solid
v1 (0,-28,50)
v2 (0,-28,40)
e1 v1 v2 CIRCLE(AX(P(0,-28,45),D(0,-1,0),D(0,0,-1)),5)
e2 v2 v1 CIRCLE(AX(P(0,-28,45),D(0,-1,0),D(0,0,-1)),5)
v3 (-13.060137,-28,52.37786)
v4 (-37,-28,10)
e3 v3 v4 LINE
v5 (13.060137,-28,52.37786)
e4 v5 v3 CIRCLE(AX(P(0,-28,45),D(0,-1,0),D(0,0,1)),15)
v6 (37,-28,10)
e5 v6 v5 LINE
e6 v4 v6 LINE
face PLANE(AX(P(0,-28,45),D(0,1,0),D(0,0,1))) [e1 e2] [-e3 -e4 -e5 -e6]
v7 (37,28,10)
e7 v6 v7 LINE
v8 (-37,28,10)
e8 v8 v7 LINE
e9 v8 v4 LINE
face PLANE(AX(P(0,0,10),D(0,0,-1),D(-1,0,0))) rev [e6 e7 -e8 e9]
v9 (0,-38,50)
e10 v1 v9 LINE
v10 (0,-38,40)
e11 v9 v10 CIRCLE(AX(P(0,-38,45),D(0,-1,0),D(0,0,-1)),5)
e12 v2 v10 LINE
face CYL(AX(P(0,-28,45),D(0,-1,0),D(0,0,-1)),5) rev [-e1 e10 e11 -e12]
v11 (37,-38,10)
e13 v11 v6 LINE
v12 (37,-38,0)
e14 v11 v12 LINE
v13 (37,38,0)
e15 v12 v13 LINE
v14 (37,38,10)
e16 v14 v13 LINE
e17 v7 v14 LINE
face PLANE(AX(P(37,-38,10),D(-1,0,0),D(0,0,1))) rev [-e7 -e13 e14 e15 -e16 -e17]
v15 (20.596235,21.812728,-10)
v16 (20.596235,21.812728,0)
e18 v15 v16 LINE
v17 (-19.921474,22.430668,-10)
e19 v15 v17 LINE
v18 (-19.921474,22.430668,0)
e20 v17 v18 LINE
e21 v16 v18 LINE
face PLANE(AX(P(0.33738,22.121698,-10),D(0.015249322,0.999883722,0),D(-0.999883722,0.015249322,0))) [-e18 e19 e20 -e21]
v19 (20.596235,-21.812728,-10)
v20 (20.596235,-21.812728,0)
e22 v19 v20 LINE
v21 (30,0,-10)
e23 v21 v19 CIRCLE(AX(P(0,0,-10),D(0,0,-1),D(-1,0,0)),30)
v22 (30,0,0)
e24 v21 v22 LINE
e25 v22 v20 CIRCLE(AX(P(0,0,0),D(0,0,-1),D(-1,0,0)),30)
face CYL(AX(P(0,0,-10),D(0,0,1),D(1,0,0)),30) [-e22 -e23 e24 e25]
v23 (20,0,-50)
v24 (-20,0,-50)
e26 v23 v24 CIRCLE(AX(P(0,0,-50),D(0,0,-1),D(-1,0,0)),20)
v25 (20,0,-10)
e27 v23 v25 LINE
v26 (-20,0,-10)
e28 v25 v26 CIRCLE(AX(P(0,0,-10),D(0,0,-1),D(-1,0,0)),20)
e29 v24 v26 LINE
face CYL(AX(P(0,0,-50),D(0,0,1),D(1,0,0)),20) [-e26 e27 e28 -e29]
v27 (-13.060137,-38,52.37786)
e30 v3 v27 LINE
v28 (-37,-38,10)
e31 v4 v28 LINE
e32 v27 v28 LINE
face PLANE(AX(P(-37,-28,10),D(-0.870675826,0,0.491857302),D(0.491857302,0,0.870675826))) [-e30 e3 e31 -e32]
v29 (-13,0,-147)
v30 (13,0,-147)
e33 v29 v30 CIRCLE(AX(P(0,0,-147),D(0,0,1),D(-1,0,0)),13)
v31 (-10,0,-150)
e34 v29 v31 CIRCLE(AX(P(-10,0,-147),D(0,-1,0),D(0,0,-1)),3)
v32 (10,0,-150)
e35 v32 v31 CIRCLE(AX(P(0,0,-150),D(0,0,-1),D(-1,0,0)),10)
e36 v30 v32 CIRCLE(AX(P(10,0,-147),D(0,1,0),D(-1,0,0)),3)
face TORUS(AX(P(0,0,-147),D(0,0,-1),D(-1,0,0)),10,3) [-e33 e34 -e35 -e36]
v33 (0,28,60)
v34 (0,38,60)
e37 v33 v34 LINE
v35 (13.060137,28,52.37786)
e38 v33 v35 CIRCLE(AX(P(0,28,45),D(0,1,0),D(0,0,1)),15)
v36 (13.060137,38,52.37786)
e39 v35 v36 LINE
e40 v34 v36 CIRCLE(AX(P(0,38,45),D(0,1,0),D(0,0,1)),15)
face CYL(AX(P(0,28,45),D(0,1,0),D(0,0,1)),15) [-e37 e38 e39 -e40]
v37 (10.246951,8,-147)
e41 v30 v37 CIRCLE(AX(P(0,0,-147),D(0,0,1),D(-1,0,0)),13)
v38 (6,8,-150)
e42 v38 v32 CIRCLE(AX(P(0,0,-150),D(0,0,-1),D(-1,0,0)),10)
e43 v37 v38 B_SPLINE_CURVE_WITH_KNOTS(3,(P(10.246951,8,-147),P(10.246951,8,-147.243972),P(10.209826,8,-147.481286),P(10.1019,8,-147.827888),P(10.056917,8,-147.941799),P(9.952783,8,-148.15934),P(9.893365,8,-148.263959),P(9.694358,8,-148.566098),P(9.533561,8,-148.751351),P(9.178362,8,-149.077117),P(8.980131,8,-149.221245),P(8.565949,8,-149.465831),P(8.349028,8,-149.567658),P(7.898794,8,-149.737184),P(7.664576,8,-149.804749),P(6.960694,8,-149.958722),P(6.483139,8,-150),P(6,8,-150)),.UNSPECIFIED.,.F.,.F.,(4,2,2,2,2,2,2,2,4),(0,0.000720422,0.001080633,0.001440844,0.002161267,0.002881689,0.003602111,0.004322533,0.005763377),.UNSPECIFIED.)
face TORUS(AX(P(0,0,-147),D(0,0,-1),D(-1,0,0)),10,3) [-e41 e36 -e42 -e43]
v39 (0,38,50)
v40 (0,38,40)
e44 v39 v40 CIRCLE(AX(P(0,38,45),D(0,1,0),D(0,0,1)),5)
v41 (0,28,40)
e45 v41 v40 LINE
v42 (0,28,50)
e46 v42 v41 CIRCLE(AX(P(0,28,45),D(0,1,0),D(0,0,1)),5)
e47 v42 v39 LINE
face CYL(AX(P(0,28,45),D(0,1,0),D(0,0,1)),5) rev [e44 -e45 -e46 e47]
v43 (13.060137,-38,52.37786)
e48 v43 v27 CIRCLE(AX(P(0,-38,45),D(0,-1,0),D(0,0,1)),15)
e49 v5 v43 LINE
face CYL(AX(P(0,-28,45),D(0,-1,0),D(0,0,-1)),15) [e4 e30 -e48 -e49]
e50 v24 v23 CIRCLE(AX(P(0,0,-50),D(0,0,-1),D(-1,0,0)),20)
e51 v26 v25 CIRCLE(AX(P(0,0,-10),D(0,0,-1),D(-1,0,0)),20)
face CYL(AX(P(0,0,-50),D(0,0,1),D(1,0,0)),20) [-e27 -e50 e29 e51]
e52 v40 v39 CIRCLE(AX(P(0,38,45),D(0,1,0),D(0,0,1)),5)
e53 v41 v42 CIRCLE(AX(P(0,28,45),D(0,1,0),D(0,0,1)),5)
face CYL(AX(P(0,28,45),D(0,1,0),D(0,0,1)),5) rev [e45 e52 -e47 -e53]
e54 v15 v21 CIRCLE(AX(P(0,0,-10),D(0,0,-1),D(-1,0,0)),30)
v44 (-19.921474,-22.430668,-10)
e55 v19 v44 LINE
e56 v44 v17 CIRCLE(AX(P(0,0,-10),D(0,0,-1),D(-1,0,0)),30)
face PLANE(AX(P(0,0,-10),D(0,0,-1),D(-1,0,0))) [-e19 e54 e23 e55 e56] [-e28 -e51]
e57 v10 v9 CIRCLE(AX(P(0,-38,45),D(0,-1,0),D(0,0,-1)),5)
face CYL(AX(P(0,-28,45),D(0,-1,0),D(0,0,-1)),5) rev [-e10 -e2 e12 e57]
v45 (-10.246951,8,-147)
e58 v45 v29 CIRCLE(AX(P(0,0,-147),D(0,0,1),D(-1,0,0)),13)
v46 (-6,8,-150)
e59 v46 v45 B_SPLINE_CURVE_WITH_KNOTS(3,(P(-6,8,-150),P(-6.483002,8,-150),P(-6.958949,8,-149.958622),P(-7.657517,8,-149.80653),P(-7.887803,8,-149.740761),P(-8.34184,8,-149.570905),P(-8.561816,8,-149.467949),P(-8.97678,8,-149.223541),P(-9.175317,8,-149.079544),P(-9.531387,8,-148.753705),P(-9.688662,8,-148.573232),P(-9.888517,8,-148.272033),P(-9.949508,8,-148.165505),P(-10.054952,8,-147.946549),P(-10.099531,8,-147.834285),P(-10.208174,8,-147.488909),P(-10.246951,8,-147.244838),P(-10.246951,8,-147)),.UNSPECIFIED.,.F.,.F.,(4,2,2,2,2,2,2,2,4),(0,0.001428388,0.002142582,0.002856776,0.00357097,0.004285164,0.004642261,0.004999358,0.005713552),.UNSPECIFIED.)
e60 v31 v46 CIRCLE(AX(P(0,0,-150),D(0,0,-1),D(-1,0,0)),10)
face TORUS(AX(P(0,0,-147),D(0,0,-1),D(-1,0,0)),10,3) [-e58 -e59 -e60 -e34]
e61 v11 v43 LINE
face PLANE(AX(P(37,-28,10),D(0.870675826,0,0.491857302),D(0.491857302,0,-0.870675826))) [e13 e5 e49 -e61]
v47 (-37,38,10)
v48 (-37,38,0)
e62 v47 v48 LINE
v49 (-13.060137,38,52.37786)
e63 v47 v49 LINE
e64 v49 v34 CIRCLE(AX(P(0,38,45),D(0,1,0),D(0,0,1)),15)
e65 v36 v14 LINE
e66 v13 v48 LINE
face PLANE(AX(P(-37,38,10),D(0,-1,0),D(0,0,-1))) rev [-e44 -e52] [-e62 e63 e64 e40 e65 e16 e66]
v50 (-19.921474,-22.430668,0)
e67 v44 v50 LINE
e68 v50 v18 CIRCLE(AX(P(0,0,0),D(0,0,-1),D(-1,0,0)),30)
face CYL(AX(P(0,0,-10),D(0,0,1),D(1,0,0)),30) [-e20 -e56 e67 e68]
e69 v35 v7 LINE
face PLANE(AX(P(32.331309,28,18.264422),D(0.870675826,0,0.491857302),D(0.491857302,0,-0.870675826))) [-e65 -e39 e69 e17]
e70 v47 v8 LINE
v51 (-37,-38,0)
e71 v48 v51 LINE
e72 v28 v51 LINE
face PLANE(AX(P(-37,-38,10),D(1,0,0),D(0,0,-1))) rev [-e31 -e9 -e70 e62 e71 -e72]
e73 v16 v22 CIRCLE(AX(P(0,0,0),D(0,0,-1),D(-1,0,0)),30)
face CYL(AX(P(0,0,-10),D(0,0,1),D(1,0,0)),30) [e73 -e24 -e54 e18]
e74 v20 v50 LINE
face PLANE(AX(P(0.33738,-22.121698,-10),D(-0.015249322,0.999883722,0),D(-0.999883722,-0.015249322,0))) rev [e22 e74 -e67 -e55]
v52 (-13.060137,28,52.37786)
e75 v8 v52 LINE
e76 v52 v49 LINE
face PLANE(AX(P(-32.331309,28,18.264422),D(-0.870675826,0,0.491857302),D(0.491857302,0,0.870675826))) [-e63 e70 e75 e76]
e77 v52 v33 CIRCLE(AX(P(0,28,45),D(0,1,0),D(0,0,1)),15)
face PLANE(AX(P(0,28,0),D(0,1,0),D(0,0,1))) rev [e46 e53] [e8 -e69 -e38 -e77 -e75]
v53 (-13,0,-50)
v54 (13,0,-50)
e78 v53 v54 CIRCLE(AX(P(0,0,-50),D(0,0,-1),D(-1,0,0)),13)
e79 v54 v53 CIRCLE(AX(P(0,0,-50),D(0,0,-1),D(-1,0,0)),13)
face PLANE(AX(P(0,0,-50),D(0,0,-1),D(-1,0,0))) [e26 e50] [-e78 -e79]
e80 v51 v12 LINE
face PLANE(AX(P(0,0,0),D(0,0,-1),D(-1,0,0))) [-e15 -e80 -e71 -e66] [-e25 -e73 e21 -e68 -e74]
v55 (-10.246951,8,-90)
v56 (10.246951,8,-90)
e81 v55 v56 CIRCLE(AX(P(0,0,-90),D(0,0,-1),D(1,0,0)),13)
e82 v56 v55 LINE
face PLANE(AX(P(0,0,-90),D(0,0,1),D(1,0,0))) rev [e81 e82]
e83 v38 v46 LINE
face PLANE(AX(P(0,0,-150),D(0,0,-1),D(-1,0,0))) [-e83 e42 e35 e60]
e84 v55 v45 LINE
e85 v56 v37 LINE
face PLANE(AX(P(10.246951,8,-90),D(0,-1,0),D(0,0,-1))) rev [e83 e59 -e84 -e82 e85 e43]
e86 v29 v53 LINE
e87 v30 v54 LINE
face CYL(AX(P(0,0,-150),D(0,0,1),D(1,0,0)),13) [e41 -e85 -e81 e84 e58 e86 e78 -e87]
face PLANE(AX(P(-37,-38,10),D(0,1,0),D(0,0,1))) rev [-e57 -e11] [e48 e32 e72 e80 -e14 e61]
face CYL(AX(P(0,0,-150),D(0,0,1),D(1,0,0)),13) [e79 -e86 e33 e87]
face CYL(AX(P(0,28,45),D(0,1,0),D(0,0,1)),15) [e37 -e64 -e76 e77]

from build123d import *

# Parameters (mm, degrees)
BASE_PLATE_SKETCH_W    = 74
BASE_PLATE_SKETCH_H    = 76
BASE_PLATE_DEPTH       = 10
FLANGE_EAR_A_SKETCH_R  = 5
FLANGE_EAR_A_DEPTH     = 10
FLANGE_START           = -10
FLANGE_EAR_B_SKETCH_R  = 5
FLANGE_EAR_B_DEPTH     = 10
TRANSITION_BOSS_DEPTH  = 10
HUB_40_SKETCH_R        = 20
HUB_40_DEPTH           = 40
SHAFT_26_SKETCH_R      = 13
SHAFT_26_DEPTH         = 100
SHAFT_START            = -60
SHAFT_FLAT_CUT_DEPTH   = 60
SHAFT_EDGE_FILLET_R3_R = 3


with BuildPart() as part:
    # Base Plate Sketch → Base Plate (new body)
    with BuildSketch(Plane.XY):
        Rectangle(BASE_PLATE_SKETCH_W, BASE_PLATE_SKETCH_H)
    extrude(amount=BASE_PLATE_DEPTH)

    # Flange Ear A Sketch → Flange Ear A (add)
    with BuildSketch(Plane(origin=(0, 38, 0), x_dir=(1, 0, 0), z_dir=(0, 1, 0))):
        with BuildLine():
            Line((-37, -10), (-13.060137394, -52.377859531))
            ThreePointArc((-13.060137394, -52.377859531), (0, -60), (13.060137394, -52.377859531))
            Line((13.060137394, -52.377859531), (37, -10))
            Line((37, -10), (-37, -10))
        make_face()
        with Locations(Location((0, -45, 0), (0, 0, 270))):
            Circle(FLANGE_EAR_A_SKETCH_R, mode=Mode.SUBTRACT)
    extrude(amount=-FLANGE_EAR_A_DEPTH)

    # Flange Ear B Sketch → Flange Ear B (add)
    with BuildSketch(Plane.XZ.offset(38).offset(FLANGE_START)):
        with BuildLine():
            Line((-37, 10), (-13.060137394, 52.377859531))
            ThreePointArc((-13.060137394, 52.377859531), (0, 60), (13.060137394, 52.377859531))
            Line((13.060137394, 52.377859531), (37, 10))
            Line((37, 10), (-37, 10))
        make_face()
        with Locations(Location((0, 45, 0), (0, 0, 90))):
            Circle(FLANGE_EAR_B_SKETCH_R, mode=Mode.SUBTRACT)
    extrude(amount=FLANGE_EAR_B_DEPTH)

    # Transition Boss Sketch → Transition Boss (add)
    with BuildSketch(Plane(origin=(0, 0, 0), x_dir=(-1, 0, 0), z_dir=(0, 0, -1))):
        with BuildLine():
            Line((19.921474427, 22.430667771), (-20.596234674, 21.812728331))
            ThreePointArc((-20.596234674, 21.812728331), (-22.10962434, 20.277191904), (-23.508824666, 18.636930081))
            ThreePointArc((-23.508824666, 18.636930081), (-30, 0), (-23.508824666, -18.636930081))
            ThreePointArc((-23.508824666, -18.636930081), (-22.10962434, -20.277191904), (-20.596234674, -21.812728331))
            Line((-20.596234674, -21.812728331), (19.921474427, -22.430667771))
            ThreePointArc((19.921474427, -22.430667771), (21.797840059, -20.611990897), (23.508824666, -18.636930081))
            ThreePointArc((23.508824666, -18.636930081), (30, 0), (23.508824666, 18.636930081))
            ThreePointArc((23.508824666, 18.636930081), (21.797840059, 20.611990897), (19.921474427, 22.430667771))
        make_face()
    extrude(amount=TRANSITION_BOSS_DEPTH)

    # Hub _40 Sketch → Hub _40 (add)
    with BuildSketch(Plane(origin=(0, 0, -10), x_dir=(-1, 0, 0), z_dir=(0, 0, -1))):
        Circle(HUB_40_SKETCH_R)
    extrude(amount=HUB_40_DEPTH)

    # Shaft _26 Sketch → Shaft _26 (add)
    with BuildSketch(Plane(origin=(0, 0, -50), x_dir=(-1, 0, 0), z_dir=(0, 0, -1))):
        Circle(SHAFT_26_SKETCH_R)
    extrude(amount=SHAFT_26_DEPTH)

    # Shaft Flat Sketch → Shaft Flat Cut (cut)
    with BuildSketch(Plane(origin=(0, 0, -150), x_dir=(-1, 0, 0), z_dir=(0, 0, -1)).offset(SHAFT_START)):
        with BuildLine():
            Line((-10.246950766, 8), (10.246950766, 8))
            ThreePointArc((10.246950766, 8), (0, 13), (-10.246950766, 8))
        make_face()
    extrude(amount=SHAFT_FLAT_CUT_DEPTH, mode=Mode.SUBTRACT)

    # Shaft Edge Fillet R3
    shaft_edge_fillet_r3_edges = [part.edges().sort_by_distance(p)[0] for p in [
        (4.230226947, -12.292484695, -150),
    ]]
    fillet(shaft_edge_fillet_r3_edges, radius=SHAFT_EDGE_FILLET_R3_R)


solid = part.part
